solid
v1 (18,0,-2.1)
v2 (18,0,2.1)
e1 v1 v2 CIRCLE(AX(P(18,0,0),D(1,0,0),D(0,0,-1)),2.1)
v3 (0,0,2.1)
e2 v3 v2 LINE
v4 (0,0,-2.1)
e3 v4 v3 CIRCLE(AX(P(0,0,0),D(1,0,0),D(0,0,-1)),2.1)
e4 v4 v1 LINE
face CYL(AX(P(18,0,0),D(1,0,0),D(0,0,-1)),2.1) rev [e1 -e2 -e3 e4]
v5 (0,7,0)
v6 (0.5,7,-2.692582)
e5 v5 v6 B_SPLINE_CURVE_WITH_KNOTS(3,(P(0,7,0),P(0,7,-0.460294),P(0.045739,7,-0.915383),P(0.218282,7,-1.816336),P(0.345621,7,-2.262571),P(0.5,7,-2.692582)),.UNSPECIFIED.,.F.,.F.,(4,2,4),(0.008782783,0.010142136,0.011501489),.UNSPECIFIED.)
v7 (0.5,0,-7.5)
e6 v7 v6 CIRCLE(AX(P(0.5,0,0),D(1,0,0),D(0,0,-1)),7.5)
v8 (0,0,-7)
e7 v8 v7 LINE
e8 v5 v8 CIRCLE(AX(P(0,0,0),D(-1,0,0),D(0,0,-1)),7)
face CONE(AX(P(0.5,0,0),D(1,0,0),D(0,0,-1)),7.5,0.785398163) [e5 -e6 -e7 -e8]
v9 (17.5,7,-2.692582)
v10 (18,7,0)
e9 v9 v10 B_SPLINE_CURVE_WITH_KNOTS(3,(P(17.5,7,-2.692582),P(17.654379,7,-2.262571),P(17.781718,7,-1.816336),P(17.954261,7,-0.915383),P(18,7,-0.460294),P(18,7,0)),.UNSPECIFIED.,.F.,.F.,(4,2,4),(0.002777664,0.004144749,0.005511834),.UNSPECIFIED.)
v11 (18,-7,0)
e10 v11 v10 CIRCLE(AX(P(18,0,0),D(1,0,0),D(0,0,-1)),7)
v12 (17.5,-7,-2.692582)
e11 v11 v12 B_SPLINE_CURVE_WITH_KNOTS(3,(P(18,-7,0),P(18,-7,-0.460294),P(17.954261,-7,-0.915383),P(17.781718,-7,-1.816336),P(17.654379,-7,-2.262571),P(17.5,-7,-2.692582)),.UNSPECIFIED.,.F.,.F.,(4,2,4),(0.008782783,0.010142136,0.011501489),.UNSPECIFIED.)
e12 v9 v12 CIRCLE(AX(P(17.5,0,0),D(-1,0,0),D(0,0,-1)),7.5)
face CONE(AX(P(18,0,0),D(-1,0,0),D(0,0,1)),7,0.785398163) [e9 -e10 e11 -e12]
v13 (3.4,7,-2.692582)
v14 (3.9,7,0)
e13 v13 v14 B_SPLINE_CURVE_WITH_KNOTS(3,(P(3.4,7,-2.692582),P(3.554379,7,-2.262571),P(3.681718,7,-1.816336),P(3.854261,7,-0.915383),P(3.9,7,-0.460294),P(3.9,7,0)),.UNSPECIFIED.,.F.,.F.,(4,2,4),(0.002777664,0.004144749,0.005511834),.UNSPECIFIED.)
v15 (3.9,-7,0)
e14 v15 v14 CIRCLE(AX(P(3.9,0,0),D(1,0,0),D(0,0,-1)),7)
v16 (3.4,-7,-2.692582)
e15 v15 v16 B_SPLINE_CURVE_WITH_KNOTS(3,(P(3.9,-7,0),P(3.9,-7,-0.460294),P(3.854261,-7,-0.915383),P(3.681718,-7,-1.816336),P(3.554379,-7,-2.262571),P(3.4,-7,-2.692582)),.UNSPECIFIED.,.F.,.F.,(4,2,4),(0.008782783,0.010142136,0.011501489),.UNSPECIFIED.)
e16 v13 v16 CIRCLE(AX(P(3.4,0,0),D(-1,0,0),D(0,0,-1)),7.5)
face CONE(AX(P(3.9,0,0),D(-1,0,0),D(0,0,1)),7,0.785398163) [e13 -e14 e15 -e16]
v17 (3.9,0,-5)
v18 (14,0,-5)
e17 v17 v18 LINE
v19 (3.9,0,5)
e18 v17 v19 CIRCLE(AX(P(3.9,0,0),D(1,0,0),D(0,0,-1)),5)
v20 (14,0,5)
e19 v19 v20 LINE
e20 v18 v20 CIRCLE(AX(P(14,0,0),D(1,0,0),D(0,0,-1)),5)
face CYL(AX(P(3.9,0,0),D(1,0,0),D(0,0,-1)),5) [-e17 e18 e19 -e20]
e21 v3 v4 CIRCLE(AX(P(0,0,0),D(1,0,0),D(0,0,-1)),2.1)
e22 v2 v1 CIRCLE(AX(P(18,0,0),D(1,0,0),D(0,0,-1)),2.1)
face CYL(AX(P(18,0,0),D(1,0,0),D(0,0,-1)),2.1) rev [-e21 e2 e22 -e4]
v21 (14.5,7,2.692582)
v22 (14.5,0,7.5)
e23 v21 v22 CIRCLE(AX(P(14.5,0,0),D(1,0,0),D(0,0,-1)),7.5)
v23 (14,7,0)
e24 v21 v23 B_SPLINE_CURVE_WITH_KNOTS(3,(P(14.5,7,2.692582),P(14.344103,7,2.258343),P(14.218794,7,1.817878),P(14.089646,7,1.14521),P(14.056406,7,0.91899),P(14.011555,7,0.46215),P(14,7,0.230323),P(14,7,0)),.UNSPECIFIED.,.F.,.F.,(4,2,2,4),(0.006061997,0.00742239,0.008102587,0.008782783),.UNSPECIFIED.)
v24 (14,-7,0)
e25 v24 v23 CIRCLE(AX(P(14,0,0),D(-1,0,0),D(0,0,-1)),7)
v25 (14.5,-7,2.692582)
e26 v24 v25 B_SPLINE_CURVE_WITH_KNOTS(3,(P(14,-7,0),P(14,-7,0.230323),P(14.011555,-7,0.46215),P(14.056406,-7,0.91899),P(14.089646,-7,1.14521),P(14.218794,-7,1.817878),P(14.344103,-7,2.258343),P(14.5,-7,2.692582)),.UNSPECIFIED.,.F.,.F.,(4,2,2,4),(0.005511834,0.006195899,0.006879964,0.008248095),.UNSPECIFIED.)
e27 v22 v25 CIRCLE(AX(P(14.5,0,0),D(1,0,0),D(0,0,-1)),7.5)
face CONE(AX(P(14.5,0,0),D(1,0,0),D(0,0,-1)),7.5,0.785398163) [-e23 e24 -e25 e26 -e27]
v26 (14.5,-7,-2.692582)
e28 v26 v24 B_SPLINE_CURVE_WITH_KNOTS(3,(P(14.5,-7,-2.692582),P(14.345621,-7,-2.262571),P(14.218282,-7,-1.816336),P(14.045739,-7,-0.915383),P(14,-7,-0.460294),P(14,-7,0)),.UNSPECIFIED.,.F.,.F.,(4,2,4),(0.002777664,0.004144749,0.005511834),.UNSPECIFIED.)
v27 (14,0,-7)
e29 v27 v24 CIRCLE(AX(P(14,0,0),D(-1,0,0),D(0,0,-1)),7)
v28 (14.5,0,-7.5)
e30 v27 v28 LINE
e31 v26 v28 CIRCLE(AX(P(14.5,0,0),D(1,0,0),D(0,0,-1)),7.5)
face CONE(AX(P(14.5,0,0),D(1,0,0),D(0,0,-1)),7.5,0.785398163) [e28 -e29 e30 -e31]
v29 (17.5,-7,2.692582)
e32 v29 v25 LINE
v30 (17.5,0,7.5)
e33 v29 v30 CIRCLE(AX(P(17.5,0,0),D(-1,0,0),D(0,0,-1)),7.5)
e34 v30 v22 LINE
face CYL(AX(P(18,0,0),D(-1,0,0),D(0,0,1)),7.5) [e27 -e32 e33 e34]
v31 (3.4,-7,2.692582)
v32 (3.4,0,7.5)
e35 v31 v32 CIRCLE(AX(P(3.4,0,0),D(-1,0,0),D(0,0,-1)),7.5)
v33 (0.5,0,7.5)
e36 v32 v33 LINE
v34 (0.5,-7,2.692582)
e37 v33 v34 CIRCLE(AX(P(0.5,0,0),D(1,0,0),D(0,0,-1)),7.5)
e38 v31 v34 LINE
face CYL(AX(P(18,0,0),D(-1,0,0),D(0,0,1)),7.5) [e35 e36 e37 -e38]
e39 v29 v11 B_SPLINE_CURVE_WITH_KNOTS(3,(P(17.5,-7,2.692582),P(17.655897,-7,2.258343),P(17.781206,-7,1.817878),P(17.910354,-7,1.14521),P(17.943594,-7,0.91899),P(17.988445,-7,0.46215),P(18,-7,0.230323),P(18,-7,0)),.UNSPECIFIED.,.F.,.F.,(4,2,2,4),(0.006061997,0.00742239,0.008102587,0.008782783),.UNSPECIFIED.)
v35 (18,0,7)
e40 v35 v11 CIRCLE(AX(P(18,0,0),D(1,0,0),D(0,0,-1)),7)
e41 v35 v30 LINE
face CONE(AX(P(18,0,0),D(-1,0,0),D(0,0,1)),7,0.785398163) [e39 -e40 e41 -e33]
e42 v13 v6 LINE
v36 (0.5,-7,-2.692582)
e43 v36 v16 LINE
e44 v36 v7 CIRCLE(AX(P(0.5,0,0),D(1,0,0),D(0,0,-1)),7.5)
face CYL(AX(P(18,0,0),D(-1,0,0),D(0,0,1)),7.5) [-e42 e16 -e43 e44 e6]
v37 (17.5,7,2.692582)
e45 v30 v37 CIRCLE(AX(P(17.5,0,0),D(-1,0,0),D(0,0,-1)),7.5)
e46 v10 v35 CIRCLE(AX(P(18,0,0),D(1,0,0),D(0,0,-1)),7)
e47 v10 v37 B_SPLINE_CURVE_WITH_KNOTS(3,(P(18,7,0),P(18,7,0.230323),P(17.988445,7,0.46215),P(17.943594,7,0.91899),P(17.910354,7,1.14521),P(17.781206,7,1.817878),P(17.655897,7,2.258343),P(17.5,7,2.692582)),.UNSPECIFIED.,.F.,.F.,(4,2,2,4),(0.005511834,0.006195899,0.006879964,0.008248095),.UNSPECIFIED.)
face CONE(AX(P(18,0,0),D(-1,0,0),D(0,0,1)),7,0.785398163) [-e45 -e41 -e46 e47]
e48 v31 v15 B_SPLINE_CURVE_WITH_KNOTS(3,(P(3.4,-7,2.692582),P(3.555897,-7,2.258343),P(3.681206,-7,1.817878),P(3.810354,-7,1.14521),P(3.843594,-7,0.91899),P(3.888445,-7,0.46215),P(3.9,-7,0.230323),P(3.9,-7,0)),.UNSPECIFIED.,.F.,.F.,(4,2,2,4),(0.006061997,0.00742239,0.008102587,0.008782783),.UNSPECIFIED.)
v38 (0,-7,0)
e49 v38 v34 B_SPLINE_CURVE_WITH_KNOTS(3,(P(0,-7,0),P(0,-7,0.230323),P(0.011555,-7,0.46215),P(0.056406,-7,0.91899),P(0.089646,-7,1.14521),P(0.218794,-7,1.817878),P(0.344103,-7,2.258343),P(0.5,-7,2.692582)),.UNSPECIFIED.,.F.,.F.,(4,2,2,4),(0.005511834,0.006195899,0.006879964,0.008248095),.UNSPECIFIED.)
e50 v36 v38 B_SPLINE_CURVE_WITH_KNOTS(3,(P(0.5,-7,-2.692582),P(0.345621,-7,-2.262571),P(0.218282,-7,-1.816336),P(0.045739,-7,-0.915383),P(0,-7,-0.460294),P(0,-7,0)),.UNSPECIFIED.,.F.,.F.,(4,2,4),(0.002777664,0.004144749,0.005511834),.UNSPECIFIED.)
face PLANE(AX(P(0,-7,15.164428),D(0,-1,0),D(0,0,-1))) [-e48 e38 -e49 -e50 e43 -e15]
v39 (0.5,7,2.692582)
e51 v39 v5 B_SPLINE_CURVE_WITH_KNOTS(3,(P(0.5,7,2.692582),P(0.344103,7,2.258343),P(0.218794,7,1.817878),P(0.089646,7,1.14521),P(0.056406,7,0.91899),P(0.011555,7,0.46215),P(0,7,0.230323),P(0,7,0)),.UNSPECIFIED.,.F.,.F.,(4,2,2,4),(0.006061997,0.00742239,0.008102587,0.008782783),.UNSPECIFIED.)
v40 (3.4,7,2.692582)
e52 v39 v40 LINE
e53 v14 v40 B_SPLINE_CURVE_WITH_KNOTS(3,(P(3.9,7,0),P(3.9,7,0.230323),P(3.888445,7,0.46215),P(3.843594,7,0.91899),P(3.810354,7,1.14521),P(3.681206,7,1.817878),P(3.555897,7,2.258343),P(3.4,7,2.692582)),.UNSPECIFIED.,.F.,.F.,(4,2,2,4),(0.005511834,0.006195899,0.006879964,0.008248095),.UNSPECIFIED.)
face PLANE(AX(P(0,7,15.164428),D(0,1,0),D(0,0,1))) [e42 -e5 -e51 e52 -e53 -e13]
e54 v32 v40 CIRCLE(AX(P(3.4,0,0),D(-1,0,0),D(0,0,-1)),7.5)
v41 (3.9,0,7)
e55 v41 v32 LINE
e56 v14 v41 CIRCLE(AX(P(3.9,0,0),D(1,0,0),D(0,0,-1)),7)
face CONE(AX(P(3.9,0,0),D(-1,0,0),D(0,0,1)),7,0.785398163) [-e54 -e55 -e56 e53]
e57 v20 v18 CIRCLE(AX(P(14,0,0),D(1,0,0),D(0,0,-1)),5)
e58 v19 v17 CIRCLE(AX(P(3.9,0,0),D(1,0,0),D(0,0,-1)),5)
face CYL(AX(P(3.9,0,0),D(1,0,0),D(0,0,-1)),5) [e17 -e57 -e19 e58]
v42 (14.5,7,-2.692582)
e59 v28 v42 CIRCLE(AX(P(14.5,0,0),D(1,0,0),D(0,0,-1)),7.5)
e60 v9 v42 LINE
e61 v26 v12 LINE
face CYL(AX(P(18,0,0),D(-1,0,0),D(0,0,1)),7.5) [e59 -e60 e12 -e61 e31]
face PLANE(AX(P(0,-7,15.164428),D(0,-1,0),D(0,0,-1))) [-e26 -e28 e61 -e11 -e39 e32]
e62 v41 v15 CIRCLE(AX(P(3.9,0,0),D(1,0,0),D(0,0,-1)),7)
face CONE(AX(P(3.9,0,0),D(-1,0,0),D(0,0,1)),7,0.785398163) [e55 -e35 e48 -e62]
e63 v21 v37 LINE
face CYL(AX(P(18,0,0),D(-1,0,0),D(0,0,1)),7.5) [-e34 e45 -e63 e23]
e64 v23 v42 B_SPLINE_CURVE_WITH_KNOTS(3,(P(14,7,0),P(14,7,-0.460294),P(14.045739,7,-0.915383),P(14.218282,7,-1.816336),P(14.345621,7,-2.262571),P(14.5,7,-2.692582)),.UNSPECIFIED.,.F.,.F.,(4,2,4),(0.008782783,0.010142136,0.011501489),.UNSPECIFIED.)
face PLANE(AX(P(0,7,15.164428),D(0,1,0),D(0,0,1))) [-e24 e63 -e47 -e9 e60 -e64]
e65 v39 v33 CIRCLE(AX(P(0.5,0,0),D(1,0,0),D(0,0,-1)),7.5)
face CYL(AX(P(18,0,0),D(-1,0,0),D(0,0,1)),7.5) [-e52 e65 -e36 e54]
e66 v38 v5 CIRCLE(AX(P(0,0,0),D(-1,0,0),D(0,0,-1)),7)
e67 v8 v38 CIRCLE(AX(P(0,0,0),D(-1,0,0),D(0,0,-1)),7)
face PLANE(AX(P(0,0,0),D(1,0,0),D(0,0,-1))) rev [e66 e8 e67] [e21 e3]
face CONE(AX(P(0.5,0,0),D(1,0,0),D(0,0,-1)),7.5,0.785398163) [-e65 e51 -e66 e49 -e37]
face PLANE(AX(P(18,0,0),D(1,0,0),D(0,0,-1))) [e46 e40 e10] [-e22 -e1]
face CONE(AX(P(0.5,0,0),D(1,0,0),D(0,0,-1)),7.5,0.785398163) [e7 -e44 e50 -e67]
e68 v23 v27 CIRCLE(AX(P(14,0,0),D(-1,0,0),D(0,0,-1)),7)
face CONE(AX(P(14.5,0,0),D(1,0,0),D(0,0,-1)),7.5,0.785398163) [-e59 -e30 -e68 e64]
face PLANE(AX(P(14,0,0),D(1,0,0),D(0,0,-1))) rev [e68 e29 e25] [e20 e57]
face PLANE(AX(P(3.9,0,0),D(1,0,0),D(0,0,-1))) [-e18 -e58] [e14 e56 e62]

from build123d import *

# Parameters (mm, degrees)
SKETCH_1_R           = 7.5
EXTRUDE_1_DEPTH      = 18
HOLE_WIZARD_M5_1_D   = 4.2
CUT_EXTRUDE_START    = -4
SKETCH_5_OUTSIDE_W   = 22.564
SKETCH_5_OUTSIDE_H   = 22.564
SKETCH_5_OUTSIDE_R   = 5
CUT_EXTRUDE_1_DEPTH  = 10.1
CHAMFER_1_SIZE       = 0.5
SKETCH_6_OUTSIDE_W   = 22.564
SKETCH_6_OUTSIDE_H   = 22.564
SKETCH_6_OUTSIDE_W_2 = 30.328855636
SKETCH_6_OUTSIDE_H_2 = 14
CUT_EXTRUDE_2_DEPTH  = 21.892582416


with BuildPart() as part:
    # 草图1 → 凸台-拉伸1 (new body)
    with BuildSketch(Plane(origin=(0, 0, 0), x_dir=(0, 0, -1), z_dir=(1, 0, 0))):
        Circle(SKETCH_1_R)
    extrude(amount=EXTRUDE_1_DEPTH)

    # M5 螺纹孔1 (through all)
    with Locations(Plane(origin=(18, 0, 0), x_dir=(0, 0, -1), z_dir=(1, 0, 0))):
        with Locations((0, 0)):
            Hole(HOLE_WIZARD_M5_1_D / 2)

    # 草图5 outside → 切除-拉伸1 (cut)
    with BuildSketch(Plane(origin=(18, 0, 0), x_dir=(0, 0, -1), z_dir=(1, 0, 0)).offset(CUT_EXTRUDE_START)):
        Rectangle(SKETCH_5_OUTSIDE_W, SKETCH_5_OUTSIDE_H)
        Circle(SKETCH_5_OUTSIDE_R, mode=Mode.SUBTRACT)
    extrude(amount=-CUT_EXTRUDE_1_DEPTH, mode=Mode.SUBTRACT)

    # 倒角1
    chamfer_1_edges = [part.edges().sort_by_distance(p)[0] for p in [
        (14, 0, 7.5),
        (3.9, 0, 7.5),
        (0, 0, 7.5),
        (18, 0, 7.5),
    ]]
    chamfer(chamfer_1_edges, length=CHAMFER_1_SIZE)

    # 草图6 outside → 切除-拉伸2 (cut, through all)
    with BuildSketch(Plane(origin=(18, 0, 0), x_dir=(0, 0, -1), z_dir=(1, 0, 0))):
        Rectangle(SKETCH_6_OUTSIDE_W, SKETCH_6_OUTSIDE_H)
        Rectangle(SKETCH_6_OUTSIDE_W_2, SKETCH_6_OUTSIDE_H_2, mode=Mode.SUBTRACT)
    extrude(amount=-CUT_EXTRUDE_2_DEPTH, mode=Mode.SUBTRACT)


solid = part.part
